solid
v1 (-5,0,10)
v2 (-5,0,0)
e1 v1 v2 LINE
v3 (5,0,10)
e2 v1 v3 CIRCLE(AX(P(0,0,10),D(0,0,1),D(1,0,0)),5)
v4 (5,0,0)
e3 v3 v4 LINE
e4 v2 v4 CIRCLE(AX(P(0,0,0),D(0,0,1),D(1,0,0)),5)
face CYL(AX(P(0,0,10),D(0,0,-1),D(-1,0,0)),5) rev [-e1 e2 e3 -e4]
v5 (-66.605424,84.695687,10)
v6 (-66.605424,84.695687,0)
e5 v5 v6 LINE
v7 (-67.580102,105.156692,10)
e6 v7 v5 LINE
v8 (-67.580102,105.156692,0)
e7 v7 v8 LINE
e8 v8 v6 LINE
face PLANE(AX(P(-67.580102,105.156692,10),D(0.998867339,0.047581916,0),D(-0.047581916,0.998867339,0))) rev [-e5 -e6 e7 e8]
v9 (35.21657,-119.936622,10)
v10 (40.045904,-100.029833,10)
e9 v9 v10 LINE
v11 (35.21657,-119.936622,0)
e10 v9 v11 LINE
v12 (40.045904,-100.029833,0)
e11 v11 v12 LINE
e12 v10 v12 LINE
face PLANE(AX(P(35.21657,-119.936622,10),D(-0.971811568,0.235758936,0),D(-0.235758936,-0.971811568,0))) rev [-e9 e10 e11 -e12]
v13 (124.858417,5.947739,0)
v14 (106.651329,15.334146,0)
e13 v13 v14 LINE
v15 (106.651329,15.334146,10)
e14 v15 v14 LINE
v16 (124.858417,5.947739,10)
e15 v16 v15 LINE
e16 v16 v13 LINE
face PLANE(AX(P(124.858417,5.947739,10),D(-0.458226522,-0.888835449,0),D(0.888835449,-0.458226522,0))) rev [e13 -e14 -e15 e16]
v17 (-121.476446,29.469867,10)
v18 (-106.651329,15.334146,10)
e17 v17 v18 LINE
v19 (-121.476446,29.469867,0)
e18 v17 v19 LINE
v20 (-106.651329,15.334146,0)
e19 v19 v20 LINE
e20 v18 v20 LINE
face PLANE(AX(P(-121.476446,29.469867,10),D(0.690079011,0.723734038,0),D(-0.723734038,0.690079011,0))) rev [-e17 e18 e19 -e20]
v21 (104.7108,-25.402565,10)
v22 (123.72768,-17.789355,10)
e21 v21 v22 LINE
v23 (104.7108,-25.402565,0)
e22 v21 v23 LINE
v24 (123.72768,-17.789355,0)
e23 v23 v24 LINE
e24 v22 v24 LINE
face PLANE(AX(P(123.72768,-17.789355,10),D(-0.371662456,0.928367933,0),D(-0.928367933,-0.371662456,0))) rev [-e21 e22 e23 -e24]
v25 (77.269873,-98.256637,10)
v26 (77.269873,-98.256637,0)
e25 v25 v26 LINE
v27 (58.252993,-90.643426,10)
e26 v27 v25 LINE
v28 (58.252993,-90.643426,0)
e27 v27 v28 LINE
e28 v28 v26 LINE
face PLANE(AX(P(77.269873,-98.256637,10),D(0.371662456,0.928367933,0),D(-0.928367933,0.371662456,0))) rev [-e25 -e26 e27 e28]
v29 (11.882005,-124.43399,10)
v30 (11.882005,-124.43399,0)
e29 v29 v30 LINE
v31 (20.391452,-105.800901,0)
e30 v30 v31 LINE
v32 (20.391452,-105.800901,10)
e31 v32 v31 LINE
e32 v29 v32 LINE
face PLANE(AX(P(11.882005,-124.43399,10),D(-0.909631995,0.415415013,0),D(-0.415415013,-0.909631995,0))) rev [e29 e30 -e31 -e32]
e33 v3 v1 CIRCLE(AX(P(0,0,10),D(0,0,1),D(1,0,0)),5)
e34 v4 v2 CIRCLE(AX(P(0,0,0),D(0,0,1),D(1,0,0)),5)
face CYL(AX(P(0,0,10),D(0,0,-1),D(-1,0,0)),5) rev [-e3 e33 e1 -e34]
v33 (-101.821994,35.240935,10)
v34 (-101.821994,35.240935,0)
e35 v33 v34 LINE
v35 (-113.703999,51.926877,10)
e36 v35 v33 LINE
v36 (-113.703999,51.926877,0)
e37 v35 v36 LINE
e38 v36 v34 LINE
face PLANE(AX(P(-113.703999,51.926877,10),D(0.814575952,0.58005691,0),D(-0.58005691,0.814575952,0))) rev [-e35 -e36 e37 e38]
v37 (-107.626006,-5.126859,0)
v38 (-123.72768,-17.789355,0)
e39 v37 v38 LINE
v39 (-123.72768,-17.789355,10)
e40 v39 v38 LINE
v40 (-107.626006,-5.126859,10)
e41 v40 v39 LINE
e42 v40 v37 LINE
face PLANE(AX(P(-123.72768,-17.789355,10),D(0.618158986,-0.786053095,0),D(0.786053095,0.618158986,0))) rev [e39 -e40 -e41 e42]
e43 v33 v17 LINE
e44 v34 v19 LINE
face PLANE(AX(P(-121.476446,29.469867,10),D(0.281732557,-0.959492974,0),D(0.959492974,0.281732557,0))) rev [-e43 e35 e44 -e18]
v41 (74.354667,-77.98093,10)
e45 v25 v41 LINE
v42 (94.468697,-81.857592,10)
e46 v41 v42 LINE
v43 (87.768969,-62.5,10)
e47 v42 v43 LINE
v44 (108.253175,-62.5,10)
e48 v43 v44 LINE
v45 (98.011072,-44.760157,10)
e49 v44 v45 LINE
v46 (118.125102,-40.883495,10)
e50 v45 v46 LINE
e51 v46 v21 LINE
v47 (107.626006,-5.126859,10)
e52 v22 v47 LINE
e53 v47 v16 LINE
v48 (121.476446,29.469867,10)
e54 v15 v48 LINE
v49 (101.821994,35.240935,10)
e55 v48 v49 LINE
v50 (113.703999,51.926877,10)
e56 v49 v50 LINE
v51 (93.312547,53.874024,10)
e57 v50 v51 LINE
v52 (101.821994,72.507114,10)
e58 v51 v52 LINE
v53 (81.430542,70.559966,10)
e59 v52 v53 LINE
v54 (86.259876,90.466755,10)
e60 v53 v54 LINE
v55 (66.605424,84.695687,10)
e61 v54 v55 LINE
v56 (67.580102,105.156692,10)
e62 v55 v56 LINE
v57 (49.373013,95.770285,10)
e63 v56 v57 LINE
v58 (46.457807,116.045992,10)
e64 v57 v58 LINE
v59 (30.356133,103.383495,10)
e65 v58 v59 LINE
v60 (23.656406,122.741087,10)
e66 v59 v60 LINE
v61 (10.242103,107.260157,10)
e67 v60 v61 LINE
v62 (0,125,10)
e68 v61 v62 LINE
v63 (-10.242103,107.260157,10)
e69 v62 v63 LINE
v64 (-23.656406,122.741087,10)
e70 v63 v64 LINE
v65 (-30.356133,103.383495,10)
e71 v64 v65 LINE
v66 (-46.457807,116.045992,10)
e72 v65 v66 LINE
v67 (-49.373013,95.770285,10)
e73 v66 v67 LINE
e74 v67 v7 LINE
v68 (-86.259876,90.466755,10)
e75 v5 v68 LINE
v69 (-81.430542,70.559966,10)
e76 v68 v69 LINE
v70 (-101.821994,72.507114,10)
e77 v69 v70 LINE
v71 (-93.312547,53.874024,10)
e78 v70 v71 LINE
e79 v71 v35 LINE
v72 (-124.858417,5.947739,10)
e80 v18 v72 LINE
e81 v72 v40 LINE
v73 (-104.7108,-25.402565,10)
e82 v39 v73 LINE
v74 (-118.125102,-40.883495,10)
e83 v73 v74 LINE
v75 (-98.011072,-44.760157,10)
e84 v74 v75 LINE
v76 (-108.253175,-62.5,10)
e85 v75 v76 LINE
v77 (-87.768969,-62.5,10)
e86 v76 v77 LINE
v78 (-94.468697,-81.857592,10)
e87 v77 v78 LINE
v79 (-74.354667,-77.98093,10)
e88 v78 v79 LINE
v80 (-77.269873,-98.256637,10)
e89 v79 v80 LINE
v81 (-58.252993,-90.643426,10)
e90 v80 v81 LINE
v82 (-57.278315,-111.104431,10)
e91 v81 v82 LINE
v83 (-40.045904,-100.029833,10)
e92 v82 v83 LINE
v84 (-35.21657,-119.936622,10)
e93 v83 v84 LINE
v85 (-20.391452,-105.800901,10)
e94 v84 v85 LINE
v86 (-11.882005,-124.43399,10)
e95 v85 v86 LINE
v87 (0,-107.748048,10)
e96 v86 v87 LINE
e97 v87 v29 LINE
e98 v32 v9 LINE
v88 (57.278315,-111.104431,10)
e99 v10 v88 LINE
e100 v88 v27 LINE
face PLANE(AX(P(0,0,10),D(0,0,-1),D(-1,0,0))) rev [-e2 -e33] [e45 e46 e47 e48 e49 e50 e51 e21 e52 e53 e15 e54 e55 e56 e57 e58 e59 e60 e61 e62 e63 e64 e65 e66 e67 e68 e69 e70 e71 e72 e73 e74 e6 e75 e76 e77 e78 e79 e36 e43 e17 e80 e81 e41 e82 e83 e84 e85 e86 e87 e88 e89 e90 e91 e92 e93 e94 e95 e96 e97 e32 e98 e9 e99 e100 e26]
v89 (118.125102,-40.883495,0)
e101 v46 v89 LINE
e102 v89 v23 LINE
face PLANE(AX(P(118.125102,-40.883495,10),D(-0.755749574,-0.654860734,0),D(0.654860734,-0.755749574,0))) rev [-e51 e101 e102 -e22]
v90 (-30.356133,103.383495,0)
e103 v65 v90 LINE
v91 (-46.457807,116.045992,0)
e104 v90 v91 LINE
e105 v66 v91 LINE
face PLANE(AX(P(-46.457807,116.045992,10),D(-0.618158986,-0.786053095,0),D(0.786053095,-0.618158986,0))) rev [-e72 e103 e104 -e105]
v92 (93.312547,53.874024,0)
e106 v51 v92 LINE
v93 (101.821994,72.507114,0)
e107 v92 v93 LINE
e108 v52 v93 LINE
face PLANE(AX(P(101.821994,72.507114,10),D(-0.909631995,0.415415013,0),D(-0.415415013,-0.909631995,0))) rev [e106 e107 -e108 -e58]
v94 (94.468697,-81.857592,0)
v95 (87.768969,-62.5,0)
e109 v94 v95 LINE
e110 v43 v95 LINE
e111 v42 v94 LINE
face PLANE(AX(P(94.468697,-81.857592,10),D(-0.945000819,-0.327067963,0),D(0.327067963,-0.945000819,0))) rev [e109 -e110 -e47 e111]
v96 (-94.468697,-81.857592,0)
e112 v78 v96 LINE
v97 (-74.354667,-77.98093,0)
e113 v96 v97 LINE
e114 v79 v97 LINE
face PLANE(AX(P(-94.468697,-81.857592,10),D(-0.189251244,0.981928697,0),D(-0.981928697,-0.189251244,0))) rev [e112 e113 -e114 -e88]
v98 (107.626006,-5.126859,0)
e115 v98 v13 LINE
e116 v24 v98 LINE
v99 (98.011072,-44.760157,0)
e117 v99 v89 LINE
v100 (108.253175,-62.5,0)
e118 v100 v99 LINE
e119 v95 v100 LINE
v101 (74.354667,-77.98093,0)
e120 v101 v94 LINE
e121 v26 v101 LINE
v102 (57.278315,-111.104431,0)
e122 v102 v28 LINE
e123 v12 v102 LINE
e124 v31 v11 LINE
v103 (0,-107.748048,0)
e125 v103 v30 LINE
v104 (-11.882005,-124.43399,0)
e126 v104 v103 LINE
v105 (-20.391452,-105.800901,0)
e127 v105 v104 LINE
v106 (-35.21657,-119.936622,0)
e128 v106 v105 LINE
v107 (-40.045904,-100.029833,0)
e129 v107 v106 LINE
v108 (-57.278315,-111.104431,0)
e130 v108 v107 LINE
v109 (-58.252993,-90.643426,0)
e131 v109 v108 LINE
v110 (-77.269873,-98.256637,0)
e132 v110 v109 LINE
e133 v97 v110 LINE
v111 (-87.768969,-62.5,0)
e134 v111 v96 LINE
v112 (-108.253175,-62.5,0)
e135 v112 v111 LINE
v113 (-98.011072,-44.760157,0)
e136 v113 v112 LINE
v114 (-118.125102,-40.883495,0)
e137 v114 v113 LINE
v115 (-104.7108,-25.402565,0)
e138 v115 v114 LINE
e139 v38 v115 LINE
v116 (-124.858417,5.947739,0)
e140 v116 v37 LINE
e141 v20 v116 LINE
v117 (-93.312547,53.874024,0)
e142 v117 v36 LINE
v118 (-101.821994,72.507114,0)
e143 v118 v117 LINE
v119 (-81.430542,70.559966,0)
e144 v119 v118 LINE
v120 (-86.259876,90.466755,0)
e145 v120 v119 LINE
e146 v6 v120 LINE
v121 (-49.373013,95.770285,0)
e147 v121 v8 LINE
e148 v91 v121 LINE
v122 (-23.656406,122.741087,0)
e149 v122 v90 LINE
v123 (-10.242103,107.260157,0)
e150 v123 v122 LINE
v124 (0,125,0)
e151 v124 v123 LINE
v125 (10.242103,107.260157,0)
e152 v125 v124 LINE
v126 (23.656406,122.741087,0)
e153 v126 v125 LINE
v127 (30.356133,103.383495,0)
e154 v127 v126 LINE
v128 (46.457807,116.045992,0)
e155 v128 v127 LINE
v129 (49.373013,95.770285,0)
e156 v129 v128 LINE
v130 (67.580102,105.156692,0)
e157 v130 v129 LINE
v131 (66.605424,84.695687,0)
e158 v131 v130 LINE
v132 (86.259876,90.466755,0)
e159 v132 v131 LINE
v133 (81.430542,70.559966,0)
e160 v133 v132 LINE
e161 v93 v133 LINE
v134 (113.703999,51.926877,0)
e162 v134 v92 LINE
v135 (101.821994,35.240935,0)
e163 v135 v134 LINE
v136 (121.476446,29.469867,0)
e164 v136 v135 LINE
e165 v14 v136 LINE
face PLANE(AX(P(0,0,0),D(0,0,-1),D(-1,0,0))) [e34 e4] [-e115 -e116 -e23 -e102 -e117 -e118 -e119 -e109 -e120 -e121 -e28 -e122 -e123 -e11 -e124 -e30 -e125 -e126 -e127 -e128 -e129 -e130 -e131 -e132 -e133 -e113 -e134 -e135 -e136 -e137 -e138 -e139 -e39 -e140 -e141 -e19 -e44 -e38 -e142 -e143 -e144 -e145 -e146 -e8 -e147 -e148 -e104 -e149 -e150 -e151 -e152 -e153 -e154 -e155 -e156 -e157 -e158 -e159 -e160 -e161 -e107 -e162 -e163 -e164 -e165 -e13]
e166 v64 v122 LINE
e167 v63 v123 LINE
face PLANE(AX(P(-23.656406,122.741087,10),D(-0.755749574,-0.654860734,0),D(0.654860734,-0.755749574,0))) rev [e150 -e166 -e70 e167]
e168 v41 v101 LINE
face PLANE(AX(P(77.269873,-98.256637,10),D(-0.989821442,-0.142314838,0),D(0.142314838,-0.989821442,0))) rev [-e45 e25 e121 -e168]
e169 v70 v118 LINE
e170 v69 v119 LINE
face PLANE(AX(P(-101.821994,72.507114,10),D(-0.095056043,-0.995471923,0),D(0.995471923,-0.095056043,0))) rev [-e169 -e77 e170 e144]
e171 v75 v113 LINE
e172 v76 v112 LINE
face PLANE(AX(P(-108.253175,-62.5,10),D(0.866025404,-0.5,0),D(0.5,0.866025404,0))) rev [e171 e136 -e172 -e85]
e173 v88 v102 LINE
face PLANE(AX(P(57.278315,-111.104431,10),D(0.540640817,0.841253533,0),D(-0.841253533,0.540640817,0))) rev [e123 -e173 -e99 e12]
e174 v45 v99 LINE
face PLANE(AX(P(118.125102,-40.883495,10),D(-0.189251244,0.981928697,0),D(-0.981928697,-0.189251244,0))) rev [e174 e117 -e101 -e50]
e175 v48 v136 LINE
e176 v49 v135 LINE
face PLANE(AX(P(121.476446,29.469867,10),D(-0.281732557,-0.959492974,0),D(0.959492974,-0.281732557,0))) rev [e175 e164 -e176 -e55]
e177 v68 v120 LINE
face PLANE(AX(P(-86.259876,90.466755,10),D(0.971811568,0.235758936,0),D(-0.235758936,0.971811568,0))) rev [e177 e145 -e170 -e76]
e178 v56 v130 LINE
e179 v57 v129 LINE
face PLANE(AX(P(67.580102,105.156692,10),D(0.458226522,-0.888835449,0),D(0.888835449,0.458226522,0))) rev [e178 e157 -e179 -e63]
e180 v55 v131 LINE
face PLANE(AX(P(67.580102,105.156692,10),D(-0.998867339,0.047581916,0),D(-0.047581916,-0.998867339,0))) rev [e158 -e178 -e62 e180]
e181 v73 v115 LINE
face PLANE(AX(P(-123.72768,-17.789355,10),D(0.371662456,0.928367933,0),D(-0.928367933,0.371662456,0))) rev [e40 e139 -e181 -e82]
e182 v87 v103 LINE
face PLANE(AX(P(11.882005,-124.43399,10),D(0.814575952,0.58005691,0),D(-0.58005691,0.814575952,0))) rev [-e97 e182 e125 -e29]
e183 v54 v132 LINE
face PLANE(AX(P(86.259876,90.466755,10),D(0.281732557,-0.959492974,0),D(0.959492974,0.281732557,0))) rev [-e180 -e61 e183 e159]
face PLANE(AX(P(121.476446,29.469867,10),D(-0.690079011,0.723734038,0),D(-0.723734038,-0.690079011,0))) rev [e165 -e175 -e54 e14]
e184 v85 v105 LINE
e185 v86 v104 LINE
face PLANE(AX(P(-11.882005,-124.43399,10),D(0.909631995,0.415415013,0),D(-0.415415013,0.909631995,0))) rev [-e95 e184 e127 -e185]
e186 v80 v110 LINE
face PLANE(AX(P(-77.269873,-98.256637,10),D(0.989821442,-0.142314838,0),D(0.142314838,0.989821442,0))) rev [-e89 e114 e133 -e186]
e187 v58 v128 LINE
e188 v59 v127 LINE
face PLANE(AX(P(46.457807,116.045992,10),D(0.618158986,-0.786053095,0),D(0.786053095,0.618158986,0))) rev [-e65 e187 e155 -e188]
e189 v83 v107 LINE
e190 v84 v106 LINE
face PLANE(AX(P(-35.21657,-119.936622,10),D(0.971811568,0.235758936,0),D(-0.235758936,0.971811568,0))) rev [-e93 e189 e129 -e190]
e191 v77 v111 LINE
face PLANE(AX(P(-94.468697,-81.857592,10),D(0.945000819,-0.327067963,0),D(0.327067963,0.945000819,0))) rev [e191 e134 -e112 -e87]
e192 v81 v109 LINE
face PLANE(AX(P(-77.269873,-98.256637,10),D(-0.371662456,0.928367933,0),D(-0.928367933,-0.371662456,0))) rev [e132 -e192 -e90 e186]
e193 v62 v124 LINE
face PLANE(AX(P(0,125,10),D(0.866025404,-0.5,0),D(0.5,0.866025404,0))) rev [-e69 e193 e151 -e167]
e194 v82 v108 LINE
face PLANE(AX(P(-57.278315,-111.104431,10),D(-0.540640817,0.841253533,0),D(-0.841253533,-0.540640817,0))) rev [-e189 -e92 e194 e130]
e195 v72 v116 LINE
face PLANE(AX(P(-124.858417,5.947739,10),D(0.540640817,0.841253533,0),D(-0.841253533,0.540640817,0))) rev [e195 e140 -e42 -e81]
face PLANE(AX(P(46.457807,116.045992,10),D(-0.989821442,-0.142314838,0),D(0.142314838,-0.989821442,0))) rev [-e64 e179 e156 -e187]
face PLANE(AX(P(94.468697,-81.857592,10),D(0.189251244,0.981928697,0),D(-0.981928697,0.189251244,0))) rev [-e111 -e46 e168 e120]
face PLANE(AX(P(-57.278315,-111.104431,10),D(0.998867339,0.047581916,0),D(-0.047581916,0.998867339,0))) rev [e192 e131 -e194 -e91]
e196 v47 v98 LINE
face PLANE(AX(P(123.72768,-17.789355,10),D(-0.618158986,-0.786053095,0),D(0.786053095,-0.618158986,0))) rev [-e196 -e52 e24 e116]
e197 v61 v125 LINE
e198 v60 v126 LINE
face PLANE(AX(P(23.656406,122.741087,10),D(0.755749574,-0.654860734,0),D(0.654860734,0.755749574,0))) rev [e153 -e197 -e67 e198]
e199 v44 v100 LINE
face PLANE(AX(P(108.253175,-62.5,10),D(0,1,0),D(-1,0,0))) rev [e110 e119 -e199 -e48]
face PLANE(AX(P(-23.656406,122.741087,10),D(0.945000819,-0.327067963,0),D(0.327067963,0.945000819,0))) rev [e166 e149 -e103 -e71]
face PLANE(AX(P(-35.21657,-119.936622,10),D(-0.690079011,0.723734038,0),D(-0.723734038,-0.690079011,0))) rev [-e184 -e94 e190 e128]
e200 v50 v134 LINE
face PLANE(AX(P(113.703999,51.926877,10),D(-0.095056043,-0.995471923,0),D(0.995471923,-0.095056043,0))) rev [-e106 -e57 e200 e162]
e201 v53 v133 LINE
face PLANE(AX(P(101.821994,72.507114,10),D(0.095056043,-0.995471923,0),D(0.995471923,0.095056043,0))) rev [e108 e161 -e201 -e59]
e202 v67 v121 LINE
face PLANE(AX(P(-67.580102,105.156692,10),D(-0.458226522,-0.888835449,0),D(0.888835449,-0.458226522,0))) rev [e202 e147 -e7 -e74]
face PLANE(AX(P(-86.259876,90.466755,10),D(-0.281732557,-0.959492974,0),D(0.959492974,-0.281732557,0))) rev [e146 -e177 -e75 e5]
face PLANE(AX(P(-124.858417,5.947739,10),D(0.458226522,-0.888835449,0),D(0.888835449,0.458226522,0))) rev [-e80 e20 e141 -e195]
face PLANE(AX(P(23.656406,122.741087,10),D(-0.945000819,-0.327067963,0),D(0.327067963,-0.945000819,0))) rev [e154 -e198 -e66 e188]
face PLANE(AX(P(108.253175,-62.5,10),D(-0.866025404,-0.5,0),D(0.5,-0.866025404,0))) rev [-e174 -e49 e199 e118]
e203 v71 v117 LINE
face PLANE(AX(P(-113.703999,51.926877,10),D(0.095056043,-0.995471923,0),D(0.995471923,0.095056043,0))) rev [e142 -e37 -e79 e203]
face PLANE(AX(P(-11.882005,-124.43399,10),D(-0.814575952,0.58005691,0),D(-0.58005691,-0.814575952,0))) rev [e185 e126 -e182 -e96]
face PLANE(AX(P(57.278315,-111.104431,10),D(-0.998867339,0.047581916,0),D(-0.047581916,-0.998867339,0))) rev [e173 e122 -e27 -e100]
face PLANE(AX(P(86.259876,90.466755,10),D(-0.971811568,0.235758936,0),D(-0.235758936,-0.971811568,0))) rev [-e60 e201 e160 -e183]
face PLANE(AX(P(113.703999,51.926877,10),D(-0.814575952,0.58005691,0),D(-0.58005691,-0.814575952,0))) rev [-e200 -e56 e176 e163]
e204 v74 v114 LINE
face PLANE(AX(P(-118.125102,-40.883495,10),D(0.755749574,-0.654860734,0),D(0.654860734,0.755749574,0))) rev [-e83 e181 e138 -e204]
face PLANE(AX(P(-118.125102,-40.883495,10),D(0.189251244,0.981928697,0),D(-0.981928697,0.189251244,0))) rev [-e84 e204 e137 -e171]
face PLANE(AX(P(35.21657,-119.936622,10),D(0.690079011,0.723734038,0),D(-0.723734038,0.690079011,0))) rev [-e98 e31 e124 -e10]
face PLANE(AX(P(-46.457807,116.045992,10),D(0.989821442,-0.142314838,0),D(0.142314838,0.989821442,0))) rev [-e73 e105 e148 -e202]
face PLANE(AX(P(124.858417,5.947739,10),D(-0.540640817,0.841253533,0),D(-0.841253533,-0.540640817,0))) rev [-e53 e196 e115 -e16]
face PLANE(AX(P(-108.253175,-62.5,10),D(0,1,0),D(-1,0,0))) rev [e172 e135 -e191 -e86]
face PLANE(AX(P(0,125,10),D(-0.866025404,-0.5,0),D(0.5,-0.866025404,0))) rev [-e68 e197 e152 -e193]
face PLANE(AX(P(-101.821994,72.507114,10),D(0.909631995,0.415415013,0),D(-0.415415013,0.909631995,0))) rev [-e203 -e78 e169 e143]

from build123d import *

# Parameters (mm, degrees)
SKETCH_1_R      = 5
EXTRUDE_4_DEPTH = 10


with BuildPart() as part:
    # 草图1 → 凸台-拉伸4 (new body)
    with BuildSketch(Plane.XY):
        Polygon((0, 125), (-10.24210316, 107.26015695), (-23.656405545, 122.741087158), (-30.356133186, 103.383495415), (-46.457806958, 116.045991627), (-49.373013467, 95.770284992), (-67.580102182, 105.156691604), (-66.605424401, 84.695686942), (-86.259876435, 90.466754763), (-81.430541758, 70.559966093), (-101.821994006, 72.507113696), (-93.312547172, 53.874024228), (-113.703999419, 51.926876625), (-101.821994006, 35.24093476), (-121.47644604, 29.469866939), (-106.651328683, 15.33414609), (-124.858417398, 5.947739478), (-107.626006464, -5.126858572), (-123.727680235, -17.789354784), (-104.710799954, -25.402565207), (-118.125102339, -40.883495415), (-98.011072313, -44.76015695), (-108.253175473, -62.5), (-87.768969153, -62.5), (-94.468696794, -81.857591743), (-74.354666768, -77.980930207), (-77.269873278, -98.256636843), (-58.252992997, -90.64342642), (-57.278315216, -111.104431082), (-40.045904282, -100.029833032), (-35.216569605, -119.936621702), (-20.391452248, -105.800900853), (-11.882005413, -124.433990322), (0, -107.748048456), (11.882005413, -124.433990322), (20.391452248, -105.800900853), (35.216569605, -119.936621702), (40.045904282, -100.029833032), (57.278315216, -111.104431082), (58.252992997, -90.64342642), (77.269873278, -98.256636843), (74.354666768, -77.980930207), (94.468696794, -81.857591743), (87.768969153, -62.5), (108.253175473, -62.5), (98.011072313, -44.76015695), (118.125102339, -40.883495415), (104.710799954, -25.402565207), (123.727680235, -17.789354784), (107.626006464, -5.126858572), (124.858417398, 5.947739478), (106.651328683, 15.33414609), (121.47644604, 29.469866939), (101.821994006, 35.24093476), (113.703999419, 51.926876625), (93.312547172, 53.874024228), (101.821994006, 72.507113696), (81.430541758, 70.559966093), (86.259876435, 90.466754763), (66.605424401, 84.695686942), (67.580102182, 105.156691604), (49.373013467, 95.770284992), (46.457806958, 116.045991627), (30.356133186, 103.383495415), (23.656405545, 122.741087158), (10.24210316, 107.26015695), align=None)
        Circle(SKETCH_1_R, mode=Mode.SUBTRACT)
    extrude(amount=EXTRUDE_4_DEPTH)


solid = part.part
